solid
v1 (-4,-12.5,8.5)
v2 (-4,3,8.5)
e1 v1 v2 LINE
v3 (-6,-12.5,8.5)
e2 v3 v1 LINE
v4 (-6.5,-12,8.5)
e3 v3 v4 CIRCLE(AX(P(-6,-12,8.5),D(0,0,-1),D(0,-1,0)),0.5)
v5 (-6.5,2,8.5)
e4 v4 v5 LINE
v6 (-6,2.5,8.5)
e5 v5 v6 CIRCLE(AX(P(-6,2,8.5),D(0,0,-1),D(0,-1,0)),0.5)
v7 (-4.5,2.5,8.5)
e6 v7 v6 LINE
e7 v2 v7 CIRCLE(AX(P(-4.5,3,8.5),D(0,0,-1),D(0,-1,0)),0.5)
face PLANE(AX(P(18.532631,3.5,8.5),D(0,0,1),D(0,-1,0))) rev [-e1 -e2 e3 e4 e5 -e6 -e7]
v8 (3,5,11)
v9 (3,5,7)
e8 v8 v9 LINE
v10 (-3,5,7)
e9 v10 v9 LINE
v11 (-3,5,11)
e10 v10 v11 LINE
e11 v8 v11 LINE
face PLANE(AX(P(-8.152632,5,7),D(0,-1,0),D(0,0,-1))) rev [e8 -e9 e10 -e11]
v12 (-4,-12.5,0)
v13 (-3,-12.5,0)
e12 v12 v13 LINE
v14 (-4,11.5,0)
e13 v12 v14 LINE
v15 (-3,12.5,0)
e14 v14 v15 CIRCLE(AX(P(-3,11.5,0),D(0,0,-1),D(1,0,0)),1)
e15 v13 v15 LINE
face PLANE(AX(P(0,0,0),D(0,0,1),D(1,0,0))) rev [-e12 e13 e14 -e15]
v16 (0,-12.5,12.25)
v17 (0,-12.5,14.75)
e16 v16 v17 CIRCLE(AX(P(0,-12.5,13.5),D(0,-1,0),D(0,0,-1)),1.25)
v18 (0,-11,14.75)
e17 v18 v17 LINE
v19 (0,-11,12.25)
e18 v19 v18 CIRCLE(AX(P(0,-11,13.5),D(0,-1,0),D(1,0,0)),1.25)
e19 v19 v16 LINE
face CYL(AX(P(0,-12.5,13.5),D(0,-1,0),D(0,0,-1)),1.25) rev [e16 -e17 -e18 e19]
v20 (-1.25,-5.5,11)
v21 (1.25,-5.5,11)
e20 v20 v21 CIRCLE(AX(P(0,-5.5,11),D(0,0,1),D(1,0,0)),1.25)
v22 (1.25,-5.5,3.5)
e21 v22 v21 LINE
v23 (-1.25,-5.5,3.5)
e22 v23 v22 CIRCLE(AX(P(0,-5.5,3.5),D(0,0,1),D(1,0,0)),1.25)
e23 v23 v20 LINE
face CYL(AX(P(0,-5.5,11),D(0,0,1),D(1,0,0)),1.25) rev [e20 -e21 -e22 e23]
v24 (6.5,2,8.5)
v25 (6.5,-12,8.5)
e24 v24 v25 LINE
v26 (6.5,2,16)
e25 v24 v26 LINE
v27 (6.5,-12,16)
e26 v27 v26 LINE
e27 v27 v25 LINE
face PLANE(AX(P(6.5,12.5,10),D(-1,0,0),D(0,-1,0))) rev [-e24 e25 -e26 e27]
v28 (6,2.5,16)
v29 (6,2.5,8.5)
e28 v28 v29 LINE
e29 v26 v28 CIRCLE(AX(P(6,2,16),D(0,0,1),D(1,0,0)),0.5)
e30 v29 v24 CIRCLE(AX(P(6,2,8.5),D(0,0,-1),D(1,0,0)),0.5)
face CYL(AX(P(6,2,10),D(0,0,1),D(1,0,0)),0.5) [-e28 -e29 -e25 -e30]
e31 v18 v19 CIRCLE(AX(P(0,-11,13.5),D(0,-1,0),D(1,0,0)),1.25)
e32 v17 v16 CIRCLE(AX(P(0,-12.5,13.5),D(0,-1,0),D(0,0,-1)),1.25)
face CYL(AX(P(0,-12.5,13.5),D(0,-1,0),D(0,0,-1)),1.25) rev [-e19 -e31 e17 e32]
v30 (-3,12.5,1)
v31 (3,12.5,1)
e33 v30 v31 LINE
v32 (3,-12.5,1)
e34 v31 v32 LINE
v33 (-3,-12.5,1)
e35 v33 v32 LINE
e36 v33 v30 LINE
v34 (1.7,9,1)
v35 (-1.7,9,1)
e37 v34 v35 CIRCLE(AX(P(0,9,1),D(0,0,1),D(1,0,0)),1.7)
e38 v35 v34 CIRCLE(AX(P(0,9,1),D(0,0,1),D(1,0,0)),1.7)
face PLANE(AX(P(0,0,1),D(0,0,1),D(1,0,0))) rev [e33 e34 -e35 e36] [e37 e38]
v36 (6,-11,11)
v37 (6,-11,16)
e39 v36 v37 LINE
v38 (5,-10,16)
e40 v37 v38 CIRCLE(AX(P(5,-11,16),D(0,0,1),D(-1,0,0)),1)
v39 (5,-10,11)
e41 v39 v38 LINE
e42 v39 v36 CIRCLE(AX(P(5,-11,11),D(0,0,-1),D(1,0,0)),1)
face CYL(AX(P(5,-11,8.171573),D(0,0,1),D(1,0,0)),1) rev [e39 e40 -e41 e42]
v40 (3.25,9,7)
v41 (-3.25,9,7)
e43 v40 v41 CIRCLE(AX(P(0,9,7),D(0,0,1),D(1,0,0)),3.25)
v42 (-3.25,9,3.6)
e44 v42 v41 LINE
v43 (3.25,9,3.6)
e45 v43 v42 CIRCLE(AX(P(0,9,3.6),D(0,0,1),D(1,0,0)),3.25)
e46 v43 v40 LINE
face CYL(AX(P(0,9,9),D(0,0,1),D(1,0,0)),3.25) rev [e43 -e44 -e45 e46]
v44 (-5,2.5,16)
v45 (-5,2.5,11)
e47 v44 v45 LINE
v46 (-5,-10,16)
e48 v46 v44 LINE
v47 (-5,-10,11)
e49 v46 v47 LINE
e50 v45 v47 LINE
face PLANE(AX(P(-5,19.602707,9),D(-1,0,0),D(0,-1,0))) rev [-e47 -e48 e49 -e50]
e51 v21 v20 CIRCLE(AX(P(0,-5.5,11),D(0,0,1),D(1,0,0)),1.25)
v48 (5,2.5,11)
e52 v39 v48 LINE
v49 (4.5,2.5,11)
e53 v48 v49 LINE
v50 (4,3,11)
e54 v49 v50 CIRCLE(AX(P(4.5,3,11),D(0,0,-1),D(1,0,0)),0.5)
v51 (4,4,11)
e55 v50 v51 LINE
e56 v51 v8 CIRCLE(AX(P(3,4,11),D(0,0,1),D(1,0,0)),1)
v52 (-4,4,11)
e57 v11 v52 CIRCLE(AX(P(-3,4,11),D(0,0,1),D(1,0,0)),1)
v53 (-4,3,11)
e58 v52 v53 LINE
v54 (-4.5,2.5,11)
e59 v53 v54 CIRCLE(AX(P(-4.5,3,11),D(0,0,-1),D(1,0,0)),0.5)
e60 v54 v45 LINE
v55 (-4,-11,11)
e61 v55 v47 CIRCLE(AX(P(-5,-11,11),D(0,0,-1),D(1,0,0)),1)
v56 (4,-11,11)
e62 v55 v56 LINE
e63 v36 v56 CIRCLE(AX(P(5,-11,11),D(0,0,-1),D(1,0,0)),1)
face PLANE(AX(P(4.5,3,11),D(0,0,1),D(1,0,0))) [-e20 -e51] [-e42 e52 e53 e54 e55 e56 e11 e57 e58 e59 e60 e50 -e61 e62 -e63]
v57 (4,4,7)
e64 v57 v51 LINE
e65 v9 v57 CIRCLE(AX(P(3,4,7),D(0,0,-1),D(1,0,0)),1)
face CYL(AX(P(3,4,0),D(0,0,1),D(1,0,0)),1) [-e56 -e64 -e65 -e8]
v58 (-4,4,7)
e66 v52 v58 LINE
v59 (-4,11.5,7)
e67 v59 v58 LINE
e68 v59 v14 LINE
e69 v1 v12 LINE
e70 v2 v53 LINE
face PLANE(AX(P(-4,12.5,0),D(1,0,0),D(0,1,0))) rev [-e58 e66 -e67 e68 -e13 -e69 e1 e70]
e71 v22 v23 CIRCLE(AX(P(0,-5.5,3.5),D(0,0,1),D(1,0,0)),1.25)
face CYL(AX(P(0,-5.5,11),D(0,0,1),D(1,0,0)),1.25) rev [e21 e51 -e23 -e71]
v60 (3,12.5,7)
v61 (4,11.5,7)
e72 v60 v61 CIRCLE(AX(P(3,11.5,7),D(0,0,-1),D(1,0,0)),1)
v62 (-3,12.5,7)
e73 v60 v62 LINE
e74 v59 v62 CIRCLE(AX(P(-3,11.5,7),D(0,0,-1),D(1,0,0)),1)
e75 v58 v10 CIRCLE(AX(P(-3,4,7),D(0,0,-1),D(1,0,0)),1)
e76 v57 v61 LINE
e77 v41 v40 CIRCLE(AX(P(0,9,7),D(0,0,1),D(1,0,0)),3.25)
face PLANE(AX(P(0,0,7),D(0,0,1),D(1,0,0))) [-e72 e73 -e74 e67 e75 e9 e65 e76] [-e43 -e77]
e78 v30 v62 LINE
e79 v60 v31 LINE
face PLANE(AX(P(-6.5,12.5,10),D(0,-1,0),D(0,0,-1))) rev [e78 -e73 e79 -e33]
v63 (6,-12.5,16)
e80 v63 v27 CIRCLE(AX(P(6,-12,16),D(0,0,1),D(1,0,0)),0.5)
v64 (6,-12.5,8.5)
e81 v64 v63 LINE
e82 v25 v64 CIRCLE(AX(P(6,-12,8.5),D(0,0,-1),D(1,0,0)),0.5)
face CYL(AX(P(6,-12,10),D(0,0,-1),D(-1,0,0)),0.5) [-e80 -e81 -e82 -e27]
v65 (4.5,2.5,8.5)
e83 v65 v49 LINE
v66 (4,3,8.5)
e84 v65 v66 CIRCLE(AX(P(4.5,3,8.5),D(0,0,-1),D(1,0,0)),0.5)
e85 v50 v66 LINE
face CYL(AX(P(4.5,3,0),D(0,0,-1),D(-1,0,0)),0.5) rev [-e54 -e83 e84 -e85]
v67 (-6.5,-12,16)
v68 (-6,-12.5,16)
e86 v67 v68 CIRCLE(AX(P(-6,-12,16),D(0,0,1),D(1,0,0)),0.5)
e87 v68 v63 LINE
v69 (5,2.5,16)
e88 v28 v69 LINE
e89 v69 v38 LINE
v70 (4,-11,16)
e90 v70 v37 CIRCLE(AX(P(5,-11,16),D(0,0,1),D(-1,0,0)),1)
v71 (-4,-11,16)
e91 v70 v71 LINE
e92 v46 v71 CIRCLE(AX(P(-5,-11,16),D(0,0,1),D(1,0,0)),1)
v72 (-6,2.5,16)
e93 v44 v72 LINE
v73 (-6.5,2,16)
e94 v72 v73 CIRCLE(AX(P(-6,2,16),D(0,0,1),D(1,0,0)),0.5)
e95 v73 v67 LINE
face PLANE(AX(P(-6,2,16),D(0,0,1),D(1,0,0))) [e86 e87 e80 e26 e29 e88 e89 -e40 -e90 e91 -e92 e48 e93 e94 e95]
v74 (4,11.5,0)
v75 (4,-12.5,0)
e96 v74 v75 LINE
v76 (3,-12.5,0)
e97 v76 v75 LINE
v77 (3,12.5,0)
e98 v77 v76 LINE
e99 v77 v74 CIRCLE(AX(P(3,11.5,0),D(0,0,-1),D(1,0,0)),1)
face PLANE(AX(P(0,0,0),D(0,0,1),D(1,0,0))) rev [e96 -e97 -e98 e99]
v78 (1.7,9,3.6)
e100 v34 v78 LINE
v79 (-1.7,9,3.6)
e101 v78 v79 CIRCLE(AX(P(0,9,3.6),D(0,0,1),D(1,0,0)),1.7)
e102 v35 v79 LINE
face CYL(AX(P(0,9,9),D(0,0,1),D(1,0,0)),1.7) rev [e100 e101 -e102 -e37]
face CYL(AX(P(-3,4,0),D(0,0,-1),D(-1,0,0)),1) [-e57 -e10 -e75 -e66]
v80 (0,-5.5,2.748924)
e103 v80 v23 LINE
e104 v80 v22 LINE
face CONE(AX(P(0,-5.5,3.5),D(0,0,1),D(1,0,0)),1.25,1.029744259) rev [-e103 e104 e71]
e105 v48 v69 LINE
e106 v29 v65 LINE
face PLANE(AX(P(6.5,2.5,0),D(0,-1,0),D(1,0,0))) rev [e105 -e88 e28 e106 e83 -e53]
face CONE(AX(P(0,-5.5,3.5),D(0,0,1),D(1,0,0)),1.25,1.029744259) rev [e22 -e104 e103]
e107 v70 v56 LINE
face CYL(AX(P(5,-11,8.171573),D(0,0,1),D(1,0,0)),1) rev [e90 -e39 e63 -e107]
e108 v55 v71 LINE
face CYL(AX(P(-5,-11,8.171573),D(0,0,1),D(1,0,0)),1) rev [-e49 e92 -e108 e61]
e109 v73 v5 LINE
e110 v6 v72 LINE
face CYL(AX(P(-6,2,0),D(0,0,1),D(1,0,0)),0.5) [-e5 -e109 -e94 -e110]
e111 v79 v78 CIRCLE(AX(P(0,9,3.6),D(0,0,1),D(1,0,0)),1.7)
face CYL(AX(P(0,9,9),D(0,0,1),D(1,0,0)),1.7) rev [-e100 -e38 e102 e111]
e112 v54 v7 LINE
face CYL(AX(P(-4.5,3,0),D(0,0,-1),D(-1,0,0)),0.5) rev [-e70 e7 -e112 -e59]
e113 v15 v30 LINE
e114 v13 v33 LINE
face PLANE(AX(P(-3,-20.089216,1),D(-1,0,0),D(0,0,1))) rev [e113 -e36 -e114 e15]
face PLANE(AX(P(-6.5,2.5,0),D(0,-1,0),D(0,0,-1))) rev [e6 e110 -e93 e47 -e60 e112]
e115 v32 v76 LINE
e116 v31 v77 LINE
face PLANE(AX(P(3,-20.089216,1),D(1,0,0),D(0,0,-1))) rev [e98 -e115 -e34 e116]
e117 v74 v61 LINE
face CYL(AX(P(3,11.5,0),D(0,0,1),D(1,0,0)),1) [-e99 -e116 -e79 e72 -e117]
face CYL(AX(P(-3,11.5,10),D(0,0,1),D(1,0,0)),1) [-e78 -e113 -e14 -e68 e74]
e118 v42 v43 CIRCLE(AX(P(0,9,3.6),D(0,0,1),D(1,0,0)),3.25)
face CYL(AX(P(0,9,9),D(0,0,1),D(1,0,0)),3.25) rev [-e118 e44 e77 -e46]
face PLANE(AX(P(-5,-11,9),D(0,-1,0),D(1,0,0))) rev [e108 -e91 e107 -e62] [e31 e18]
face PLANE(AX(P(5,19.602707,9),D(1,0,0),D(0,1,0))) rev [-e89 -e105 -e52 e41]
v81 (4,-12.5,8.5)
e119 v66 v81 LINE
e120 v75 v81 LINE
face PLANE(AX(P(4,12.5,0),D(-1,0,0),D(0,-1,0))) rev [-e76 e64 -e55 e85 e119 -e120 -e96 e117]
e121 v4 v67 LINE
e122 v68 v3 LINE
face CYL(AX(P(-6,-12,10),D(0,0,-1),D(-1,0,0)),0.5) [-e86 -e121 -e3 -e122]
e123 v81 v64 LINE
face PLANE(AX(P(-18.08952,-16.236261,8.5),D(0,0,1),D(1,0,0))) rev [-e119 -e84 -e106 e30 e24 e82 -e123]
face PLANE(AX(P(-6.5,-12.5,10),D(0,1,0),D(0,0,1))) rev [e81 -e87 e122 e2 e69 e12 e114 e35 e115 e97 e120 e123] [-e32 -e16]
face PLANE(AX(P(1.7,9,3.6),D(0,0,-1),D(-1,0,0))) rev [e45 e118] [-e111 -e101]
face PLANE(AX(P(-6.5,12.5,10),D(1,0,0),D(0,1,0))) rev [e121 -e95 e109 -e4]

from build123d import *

# Parameters (mm, degrees)
SKETCH1_W                                           = 13
SKETCH1_H                                           = 25
BOSS_EXTRUDE1_DEPTH                                 = 10
CUT_EXTRUDE1_DEPTH                                  = 18.277152543
CUT_EXTRUDE1_DEPTH_BACK                             = 18.277152543
SKETCH2_W                                           = 2.5
SKETCH2_H                                           = 10
FILLET1_R                                           = 0.5
FILLET2_R                                           = 1
SKETCH8_W                                           = 6
SKETCH8_H                                           = 32.589216013
CUT_EXTRUDE4_DEPTH                                  = 1
SKETCH21_W                                          = 10
SKETCH21_H                                          = 30.602707306
CUT_EXTRUDE11_DEPTH                                 = 1
SKETCH25_W                                          = 13.801043237
SKETCH25_H                                          = 15.676526687
CUT_EXTRUDE13_DEPTH                                 = 2
FILLET3_R                                           = 1
CBORE_FOR_M3_HEX_SOCKET_HEAD_CAP_SCREW2_D           = 3.4
CBORE_FOR_M3_HEX_SOCKET_HEAD_CAP_SCREW2_CBORE_D     = 6.5
CBORE_FOR_M3_HEX_SOCKET_HEAD_CAP_SCREW2_CBORE_DEPTH = 5.4
BOSS_EXTRUDE4_START                                 = 6
BOSS_EXTRUDE4_DEPTH                                 = 6
CUT_EXTRUDE15_REACH                                 = 26.109
SKETCH33_W                                          = 10.378798484
SKETCH33_H                                          = 20
SKETCH34_W                                          = 9.92103125
SKETCH34_H                                          = 19.736261401
CUT_EXTRUDE16_DEPTH                                 = 2.5
BOSS_EXTRUDE5_START                                 = 2
BOSS_EXTRUDE5_DEPTH                                 = 2
M3_TAPPED_HOLE1_D                                   = 2.5
M3_TAPPED_HOLE1_DEPTH                               = 7.5
M3_TAPPED_HOLE1_TIP                                 = 0.751075774
M3_TAPPED_HOLE2_D                                   = 2.5
M3_TAPPED_HOLE2_DEPTH                               = 7.5
M3_TAPPED_HOLE2_TIP                                 = 0.751075774
SKETCH41_R                                          = 1
CUT_EXTRUDE17_DEPTH                                 = 5


with BuildPart() as part:
    # Sketch1 → Boss-Extrude1 (new body)
    with BuildSketch(Plane.XY):
        Rectangle(SKETCH1_W, SKETCH1_H)
    extrude(amount=BOSS_EXTRUDE1_DEPTH)

    # Sketch2 → Cut-Extrude1 (cut, two sides: drawn at the far end of the back side and taken through both)
    with BuildSketch(Plane.XY.offset(10).offset(-CUT_EXTRUDE1_DEPTH_BACK)):
        with Locations((-5.25, 7.5)):
            Rectangle(SKETCH2_W, SKETCH2_H)
        with Locations((5.25, 7.5)):
            Rectangle(SKETCH2_W, SKETCH2_H)
    extrude(amount=CUT_EXTRUDE1_DEPTH + CUT_EXTRUDE1_DEPTH_BACK, mode=Mode.SUBTRACT)

    # Fillet1
    fillet1_edges = [part.edges().sort_by_distance(p)[0] for p in [
        (-6.5, 2.5, 5),
        (-4, 2.5, 5),
        (6.5, 2.5, 5),
        (4, 2.5, 5),
        (6.5, -12.5, 5),
        (-6.5, -12.5, 5),
    ]]
    fillet(fillet1_edges, radius=FILLET1_R)

    # Fillet2
    fillet2_edges = [part.edges().sort_by_distance(p)[0] for p in [
        (-4, 12.5, 5),
        (4, 12.5, 5),
    ]]
    fillet(fillet2_edges, radius=FILLET2_R)

    # Sketch8 → Cut-Extrude4 (cut)
    with BuildSketch(Plane(origin=(0, 0, 0), x_dir=(-1, 0, 0), z_dir=(0, 0, -1))):
        with Locations((0, -3.794608007)):
            Rectangle(SKETCH8_W, SKETCH8_H)
    extrude(amount=-CUT_EXTRUDE4_DEPTH, mode=Mode.SUBTRACT)

    # Sketch21 → Cut-Extrude11 (cut)
    with BuildSketch(Plane.XY.offset(10)):
        with Locations((0, 4.301353653)):
            Rectangle(SKETCH21_W, SKETCH21_H)
    extrude(amount=-CUT_EXTRUDE11_DEPTH, mode=Mode.SUBTRACT)

    # Sketch25 → Cut-Extrude13 (cut)
    with BuildSketch(Plane.XY.offset(9)):
        with Locations((-1.252110778, 12.838263344)):
            Rectangle(SKETCH25_W, SKETCH25_H)
    extrude(amount=-CUT_EXTRUDE13_DEPTH, mode=Mode.SUBTRACT)

    # Fillet3
    fillet3_edges = [part.edges().sort_by_distance(p)[0] for p in [
        (4, 5, 8),
        (-4, 5, 8),
    ]]
    fillet(fillet3_edges, radius=FILLET3_R)

    # CBORE for M3 Hex Socket Head Cap Screw2 (through all)
    with Locations(Plane.XY.offset(9)):
        with Locations((0, 9)):
            CounterBoreHole(CBORE_FOR_M3_HEX_SOCKET_HEAD_CAP_SCREW2_D / 2, CBORE_FOR_M3_HEX_SOCKET_HEAD_CAP_SCREW2_CBORE_D / 2, CBORE_FOR_M3_HEX_SOCKET_HEAD_CAP_SCREW2_CBORE_DEPTH)

    # Sketch31 → Boss-Extrude4 (add)
    with BuildSketch(Plane.XY.offset(10).offset(BOSS_EXTRUDE4_START)):
        with BuildLine():
            Line((-5, -11), (-5, 2.5))
            Line((-5, 2.5), (-6, 2.5))
            ThreePointArc((-6, 2.5), (-6.353553391, 2.353553391), (-6.5, 2))
            Line((-6.5, 2), (-6.5, -12))
            ThreePointArc((-6.5, -12), (-6.353553391, -12.353553391), (-6, -12.5))
            Line((-6, -12.5), (6, -12.5))
            ThreePointArc((6, -12.5), (6.353553391, -12.353553391), (6.5, -12))
            Line((6.5, -12), (6.5, 2))
            ThreePointArc((6.5, 2), (6.353553391, 2.353553391), (6, 2.5))
            Line((6, 2.5), (5, 2.5))
            Line((5, 2.5), (5, -11))
            Line((5, -11), (-5, -11))
        make_face()
    extrude(amount=-BOSS_EXTRUDE4_DEPTH)

    # Cut-Extrude15: up to this face of the body (flat: up to its plane)
    cut_extrude15_end = Plane(part.part.faces().sort_by_distance((-4, 7.12804878, 3.646341463))[0])
    # Sketch33 → Cut-Extrude15 (cut, up to the picked face)
    with BuildSketch(Plane.ZY.offset(6.5), mode=Mode.PRIVATE) as cut_extrude15_sk1:
        with Locations((3.310600758, -6.5)):
            Rectangle(SKETCH33_W, SKETCH33_H)
    cut_extrude15_tool1 = split(extrude(cut_extrude15_sk1.sketch, amount=-CUT_EXTRUDE15_REACH, mode=Mode.PRIVATE), bisect_by=cut_extrude15_end, keep=Keep.BOTH, mode=Mode.PRIVATE)
    add(cut_extrude15_tool1.solids().sort_by(Axis((-6.5, -6.5, 3.310601), (1, 0, 0)))[0], mode=Mode.SUBTRACT)

    # Sketch34 → Cut-Extrude16 (cut)
    with BuildSketch(Plane(origin=(6.5, 0, 0), x_dir=(0, 0, -1), z_dir=(1, 0, 0))):
        with Locations((-3.539484375, -6.368130701)):
            Rectangle(SKETCH34_W, SKETCH34_H)
    extrude(amount=-CUT_EXTRUDE16_DEPTH, mode=Mode.SUBTRACT)

    # Sketch36 → Boss-Extrude5 (add)
    with BuildSketch(Plane.XY.offset(9).offset(BOSS_EXTRUDE5_START)):
        with BuildLine():
            Line((-5, 2.5), (-5, -11))
            Line((-5, -11), (5, -11))
            Line((5, -11), (5, 2.5))
            Line((5, 2.5), (4.5, 2.5))
            ThreePointArc((4.5, 2.5), (4.146446609, 2.646446609), (4, 3))
            Line((4, 3), (4, 4))
            ThreePointArc((4, 4), (3.707106781, 4.707106781), (3, 5))
            Line((3, 5), (-3, 5))
            ThreePointArc((-3, 5), (-3.707106781, 4.707106781), (-4, 4))
            Line((-4, 4), (-4, 3))
            ThreePointArc((-4, 3), (-4.146446609, 2.646446609), (-4.5, 2.5))
            Line((-4.5, 2.5), (-5, 2.5))
        make_face()
    extrude(amount=-BOSS_EXTRUDE5_DEPTH)

    # M3 Tapped Hole1
    with Locations(Plane.XY.offset(11)):
        with Locations((0, -5.5)):
            Hole(M3_TAPPED_HOLE1_D / 2, depth=M3_TAPPED_HOLE1_DEPTH)
            with Locations((0, 0, -(M3_TAPPED_HOLE1_DEPTH + M3_TAPPED_HOLE1_TIP / 2))):  # 118° drill point
                Cone(0, M3_TAPPED_HOLE1_D / 2, M3_TAPPED_HOLE1_TIP, mode=Mode.SUBTRACT)

    # M3 Tapped Hole2
    with Locations(Plane(origin=(0, -12.5, 0), x_dir=(-1, 0, 0), z_dir=(0, -1, 0))):
        with Locations((0, -13.5)):
            Hole(M3_TAPPED_HOLE2_D / 2, depth=M3_TAPPED_HOLE2_DEPTH)
            with Locations((0, 0, -(M3_TAPPED_HOLE2_DEPTH + M3_TAPPED_HOLE2_TIP / 2))):  # 118° drill point
                Cone(0, M3_TAPPED_HOLE2_D / 2, M3_TAPPED_HOLE2_TIP, mode=Mode.SUBTRACT)

    # Sketch41 → Cut-Extrude17 (cut)
    with BuildSketch(Plane.XY.offset(16)):
        with Locations((-5, -11)):
            Circle(SKETCH41_R)
        with Locations((5, -11)):
            Circle(SKETCH41_R)
    extrude(amount=-CUT_EXTRUDE17_DEPTH, mode=Mode.SUBTRACT)


solid = part.part
